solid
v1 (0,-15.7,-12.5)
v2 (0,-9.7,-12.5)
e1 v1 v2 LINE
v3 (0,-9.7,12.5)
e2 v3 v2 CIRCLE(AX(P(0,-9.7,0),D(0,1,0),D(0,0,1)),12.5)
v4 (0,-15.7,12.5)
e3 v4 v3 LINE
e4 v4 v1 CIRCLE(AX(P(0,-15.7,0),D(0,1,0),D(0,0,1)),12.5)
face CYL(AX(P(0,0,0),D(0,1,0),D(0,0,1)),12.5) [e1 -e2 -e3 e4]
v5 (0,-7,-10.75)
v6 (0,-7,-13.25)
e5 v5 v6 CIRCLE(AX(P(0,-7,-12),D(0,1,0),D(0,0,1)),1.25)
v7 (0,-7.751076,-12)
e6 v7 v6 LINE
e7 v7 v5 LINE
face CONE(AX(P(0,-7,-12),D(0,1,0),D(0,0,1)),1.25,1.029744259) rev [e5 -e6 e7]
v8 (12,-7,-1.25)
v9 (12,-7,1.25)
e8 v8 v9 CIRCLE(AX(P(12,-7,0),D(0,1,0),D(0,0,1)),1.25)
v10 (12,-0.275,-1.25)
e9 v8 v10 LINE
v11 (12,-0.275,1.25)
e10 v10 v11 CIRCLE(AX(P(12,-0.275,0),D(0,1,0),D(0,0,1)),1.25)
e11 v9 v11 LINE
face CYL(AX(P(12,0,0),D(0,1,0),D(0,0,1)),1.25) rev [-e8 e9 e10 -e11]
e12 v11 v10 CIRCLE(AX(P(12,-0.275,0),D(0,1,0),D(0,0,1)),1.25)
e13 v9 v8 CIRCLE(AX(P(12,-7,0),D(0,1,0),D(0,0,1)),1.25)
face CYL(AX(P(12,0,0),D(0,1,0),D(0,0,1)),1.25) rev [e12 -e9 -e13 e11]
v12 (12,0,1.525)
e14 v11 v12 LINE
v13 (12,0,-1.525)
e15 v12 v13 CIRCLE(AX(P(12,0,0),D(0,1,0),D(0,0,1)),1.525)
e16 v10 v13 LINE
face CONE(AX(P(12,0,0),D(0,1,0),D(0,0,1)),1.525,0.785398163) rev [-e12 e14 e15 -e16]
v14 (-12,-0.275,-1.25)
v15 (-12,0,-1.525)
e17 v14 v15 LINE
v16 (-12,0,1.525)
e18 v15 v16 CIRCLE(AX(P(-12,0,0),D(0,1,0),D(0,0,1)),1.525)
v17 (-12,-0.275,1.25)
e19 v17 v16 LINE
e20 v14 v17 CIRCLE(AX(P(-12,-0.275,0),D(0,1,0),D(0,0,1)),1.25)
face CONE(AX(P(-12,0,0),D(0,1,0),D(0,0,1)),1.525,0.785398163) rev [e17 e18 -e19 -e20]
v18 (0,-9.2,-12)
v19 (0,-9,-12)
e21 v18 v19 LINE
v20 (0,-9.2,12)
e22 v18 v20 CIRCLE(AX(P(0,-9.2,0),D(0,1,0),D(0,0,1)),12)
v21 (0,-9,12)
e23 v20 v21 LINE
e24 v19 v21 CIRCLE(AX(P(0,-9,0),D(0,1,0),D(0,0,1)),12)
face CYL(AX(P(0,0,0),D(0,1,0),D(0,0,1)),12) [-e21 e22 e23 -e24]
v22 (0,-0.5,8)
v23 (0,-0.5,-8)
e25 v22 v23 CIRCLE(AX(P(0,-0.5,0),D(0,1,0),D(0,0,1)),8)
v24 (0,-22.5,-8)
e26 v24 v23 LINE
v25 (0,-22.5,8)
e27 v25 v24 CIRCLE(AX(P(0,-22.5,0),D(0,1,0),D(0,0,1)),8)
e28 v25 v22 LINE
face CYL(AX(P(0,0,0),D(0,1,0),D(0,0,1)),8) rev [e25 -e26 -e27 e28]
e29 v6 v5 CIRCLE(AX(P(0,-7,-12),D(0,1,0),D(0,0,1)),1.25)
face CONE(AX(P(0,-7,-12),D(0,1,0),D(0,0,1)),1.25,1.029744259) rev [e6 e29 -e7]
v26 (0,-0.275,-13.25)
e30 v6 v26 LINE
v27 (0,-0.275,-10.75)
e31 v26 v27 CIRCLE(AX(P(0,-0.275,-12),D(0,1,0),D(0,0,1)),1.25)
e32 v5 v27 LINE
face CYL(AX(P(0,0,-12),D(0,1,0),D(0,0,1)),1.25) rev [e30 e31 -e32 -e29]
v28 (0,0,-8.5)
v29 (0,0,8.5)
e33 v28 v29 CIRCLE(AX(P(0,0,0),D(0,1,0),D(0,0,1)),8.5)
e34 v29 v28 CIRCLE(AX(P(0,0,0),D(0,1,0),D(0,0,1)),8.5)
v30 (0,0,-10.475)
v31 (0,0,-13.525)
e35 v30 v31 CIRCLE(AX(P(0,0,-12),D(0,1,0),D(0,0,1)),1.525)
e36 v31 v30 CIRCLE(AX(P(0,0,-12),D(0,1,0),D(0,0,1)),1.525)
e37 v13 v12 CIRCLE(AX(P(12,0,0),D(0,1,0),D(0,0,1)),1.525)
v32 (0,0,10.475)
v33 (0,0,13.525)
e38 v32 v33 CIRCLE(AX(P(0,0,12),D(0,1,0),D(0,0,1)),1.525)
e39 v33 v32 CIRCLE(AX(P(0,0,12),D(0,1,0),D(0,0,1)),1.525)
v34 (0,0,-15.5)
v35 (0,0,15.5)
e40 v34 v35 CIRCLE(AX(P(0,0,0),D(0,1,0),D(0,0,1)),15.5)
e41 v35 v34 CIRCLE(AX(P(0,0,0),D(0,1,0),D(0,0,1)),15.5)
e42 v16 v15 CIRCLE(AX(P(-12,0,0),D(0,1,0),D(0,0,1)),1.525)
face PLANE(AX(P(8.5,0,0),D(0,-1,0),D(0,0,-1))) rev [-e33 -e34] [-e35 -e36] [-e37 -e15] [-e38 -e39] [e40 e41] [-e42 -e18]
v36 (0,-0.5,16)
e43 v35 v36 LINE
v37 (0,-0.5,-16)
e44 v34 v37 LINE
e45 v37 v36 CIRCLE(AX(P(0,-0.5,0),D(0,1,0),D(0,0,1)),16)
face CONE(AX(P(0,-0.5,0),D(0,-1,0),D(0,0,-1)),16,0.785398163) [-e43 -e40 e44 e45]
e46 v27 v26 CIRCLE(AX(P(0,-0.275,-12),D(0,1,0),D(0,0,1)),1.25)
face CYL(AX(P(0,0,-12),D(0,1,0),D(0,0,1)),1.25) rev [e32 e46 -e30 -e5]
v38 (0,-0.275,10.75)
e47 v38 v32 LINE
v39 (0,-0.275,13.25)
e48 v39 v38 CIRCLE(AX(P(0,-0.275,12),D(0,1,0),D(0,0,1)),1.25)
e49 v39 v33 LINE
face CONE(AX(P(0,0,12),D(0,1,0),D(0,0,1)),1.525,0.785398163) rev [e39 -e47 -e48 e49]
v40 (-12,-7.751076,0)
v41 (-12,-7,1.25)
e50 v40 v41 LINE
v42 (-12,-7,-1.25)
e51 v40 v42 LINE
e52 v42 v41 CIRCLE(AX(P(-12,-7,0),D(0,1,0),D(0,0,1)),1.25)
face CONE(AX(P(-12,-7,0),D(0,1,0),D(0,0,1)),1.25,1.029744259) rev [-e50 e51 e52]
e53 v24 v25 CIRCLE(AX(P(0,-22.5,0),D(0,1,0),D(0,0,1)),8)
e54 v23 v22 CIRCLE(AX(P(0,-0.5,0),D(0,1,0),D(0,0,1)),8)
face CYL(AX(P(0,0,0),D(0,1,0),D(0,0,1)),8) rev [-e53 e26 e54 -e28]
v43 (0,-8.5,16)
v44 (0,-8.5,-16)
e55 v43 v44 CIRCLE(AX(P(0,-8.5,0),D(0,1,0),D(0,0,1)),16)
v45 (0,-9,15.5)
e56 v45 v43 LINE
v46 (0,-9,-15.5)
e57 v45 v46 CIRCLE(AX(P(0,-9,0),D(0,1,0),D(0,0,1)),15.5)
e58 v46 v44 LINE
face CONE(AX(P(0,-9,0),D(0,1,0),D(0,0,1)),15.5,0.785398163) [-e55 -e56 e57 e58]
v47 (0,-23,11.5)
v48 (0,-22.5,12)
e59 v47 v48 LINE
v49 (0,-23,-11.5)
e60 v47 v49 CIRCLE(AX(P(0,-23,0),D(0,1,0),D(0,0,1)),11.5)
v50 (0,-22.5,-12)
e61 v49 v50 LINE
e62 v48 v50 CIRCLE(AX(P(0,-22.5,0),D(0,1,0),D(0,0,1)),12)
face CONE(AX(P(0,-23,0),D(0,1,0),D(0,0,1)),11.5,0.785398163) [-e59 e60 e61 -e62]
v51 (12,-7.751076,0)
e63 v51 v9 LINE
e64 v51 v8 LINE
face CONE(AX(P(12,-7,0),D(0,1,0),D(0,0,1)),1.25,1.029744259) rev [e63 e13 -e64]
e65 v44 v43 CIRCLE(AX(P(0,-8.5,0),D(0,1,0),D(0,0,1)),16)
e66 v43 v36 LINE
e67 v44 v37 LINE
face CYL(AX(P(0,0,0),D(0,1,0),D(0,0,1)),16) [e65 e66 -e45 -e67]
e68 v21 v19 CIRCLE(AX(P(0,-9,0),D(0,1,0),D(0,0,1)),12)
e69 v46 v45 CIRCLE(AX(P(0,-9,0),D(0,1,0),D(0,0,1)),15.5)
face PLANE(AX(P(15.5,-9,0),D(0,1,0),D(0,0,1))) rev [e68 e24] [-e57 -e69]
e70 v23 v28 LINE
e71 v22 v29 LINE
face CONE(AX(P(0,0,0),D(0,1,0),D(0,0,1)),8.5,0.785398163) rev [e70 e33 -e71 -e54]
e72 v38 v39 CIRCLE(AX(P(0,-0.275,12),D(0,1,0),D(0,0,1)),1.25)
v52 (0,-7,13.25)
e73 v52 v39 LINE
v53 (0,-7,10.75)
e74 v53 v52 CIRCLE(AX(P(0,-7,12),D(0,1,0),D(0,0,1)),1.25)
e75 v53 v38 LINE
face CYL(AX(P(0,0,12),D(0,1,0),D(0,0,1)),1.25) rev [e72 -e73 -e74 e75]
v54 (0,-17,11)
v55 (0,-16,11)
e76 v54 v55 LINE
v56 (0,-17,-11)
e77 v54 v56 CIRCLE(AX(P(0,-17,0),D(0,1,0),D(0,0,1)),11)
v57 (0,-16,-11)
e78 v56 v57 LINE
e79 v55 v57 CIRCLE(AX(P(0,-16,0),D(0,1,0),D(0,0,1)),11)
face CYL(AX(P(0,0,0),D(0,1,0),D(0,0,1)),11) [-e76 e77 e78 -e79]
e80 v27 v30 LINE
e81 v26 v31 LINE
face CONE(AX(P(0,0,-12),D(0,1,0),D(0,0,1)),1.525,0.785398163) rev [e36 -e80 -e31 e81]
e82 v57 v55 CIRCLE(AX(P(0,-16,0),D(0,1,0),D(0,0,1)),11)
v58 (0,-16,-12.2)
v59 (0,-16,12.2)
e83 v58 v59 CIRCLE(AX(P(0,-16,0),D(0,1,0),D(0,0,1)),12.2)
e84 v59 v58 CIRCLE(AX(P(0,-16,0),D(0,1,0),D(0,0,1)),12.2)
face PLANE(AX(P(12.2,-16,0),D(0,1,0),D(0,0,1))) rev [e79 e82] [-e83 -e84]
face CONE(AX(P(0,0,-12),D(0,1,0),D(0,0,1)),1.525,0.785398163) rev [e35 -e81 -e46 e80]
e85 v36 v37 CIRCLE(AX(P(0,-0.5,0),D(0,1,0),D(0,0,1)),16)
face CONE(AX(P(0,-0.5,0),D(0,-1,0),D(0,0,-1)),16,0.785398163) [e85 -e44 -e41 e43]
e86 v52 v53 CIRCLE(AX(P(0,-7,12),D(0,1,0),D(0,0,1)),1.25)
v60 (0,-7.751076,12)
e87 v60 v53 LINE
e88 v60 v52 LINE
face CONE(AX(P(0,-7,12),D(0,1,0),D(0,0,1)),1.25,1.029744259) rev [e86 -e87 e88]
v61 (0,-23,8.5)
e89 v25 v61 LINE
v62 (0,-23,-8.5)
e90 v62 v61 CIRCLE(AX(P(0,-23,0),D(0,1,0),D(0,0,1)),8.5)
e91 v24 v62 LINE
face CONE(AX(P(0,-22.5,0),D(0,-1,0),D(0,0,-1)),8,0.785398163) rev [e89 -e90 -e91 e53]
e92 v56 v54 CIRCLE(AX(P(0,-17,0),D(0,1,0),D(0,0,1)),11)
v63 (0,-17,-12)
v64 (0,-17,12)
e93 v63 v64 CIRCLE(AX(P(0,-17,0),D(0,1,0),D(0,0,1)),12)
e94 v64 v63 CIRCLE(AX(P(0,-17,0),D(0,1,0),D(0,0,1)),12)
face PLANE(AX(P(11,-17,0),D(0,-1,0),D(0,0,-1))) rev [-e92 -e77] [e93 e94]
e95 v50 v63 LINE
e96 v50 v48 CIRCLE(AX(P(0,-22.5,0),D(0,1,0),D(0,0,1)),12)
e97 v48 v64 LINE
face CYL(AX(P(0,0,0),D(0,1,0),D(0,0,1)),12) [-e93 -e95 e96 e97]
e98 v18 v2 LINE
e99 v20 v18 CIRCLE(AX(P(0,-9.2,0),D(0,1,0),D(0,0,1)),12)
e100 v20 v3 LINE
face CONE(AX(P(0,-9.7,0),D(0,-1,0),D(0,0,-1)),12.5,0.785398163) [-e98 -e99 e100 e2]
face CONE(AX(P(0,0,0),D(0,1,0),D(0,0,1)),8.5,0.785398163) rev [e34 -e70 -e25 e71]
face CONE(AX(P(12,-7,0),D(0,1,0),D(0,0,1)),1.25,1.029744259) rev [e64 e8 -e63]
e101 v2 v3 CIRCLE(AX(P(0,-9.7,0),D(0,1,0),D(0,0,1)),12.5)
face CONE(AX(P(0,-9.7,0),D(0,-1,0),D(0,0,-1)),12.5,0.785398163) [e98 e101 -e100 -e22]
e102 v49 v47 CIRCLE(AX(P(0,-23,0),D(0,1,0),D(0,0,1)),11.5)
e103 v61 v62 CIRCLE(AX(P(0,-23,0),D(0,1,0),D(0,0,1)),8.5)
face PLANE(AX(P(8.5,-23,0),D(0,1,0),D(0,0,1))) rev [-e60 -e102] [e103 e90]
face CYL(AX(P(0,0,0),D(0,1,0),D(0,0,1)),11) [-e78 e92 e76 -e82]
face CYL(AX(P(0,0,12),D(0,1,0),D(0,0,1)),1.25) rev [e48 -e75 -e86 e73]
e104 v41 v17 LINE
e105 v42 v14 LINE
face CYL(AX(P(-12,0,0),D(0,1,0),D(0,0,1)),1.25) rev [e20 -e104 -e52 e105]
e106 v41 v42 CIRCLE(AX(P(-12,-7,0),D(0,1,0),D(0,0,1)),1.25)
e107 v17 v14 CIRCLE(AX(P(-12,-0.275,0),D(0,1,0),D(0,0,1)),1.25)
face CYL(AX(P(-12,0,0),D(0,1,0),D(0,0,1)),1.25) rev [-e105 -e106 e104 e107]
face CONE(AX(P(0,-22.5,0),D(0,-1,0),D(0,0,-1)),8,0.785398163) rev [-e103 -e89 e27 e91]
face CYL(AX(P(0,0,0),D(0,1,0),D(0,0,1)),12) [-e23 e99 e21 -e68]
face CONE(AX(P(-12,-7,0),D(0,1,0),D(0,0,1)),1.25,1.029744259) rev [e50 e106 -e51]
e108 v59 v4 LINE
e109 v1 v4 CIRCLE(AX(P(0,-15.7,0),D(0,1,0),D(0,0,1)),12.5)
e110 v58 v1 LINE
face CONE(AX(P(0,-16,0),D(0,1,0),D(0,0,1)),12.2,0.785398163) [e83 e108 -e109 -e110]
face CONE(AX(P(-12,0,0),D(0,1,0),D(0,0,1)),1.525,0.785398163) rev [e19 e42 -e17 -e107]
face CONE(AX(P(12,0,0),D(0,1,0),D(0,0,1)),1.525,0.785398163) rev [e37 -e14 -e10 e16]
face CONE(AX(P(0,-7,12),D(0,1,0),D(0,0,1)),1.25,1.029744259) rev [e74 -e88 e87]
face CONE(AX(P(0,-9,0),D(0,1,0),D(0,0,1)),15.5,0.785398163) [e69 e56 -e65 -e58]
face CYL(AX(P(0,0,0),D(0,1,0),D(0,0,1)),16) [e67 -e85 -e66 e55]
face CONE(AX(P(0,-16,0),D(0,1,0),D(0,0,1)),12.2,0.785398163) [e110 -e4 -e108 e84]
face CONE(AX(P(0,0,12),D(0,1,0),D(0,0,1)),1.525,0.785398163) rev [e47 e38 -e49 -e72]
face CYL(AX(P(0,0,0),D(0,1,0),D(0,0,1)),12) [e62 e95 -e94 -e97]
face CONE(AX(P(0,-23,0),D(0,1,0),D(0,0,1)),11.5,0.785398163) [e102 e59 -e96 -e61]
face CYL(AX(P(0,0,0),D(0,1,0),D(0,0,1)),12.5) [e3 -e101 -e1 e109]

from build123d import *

# Parameters (mm, degrees)
M3_TAPPED_HOLE1_D           = 2.5
M3_TAPPED_HOLE1_DEPTH       = 7
M3_TAPPED_HOLE1_CSINK_D     = 3.05
M3_TAPPED_HOLE1_CSINK_ANGLE = 90
M3_TAPPED_HOLE1_TIP         = 0.751075774


with BuildPart() as part:
    # Sketch1 → Revolve1 (revolve)
    with BuildSketch(Plane.XY, mode=Mode.PRIVATE) as revolve1_sk:
        Polygon((8.5, 0), (15.5, 0), (16, -0.5), (16, -8.5), (15.5, -9), (12, -9), (12, -9.2), (12.5, -9.7), (12.5, -15.7), (12.2, -16), (11, -16), (11, -17), (12, -17), (12, -22.5), (11.5, -23), (8.5, -23), (8, -22.5), (8, -0.5), align=None)
    revolve(revolve1_sk.sketch.rotate(Axis((0, 0, 0), (0, -1, 0)), 90), axis=Axis((0, 0, 0), (0, -1, 0)))

    # M3 Tapped Hole1
    with Locations(Plane(origin=(0, 0, 0), x_dir=(1, 0, 0), z_dir=(0, 1, 0))):
        with Locations((-12, 0), (0, 12), (12, 0), (0, -12)):
            CounterSinkHole(M3_TAPPED_HOLE1_D / 2, M3_TAPPED_HOLE1_CSINK_D / 2, depth=M3_TAPPED_HOLE1_DEPTH, counter_sink_angle=M3_TAPPED_HOLE1_CSINK_ANGLE)
            with Locations((0, 0, -(M3_TAPPED_HOLE1_DEPTH + M3_TAPPED_HOLE1_TIP / 2))):  # 118° drill point
                Cone(0, M3_TAPPED_HOLE1_D / 2, M3_TAPPED_HOLE1_TIP, mode=Mode.SUBTRACT)


solid = part.part
